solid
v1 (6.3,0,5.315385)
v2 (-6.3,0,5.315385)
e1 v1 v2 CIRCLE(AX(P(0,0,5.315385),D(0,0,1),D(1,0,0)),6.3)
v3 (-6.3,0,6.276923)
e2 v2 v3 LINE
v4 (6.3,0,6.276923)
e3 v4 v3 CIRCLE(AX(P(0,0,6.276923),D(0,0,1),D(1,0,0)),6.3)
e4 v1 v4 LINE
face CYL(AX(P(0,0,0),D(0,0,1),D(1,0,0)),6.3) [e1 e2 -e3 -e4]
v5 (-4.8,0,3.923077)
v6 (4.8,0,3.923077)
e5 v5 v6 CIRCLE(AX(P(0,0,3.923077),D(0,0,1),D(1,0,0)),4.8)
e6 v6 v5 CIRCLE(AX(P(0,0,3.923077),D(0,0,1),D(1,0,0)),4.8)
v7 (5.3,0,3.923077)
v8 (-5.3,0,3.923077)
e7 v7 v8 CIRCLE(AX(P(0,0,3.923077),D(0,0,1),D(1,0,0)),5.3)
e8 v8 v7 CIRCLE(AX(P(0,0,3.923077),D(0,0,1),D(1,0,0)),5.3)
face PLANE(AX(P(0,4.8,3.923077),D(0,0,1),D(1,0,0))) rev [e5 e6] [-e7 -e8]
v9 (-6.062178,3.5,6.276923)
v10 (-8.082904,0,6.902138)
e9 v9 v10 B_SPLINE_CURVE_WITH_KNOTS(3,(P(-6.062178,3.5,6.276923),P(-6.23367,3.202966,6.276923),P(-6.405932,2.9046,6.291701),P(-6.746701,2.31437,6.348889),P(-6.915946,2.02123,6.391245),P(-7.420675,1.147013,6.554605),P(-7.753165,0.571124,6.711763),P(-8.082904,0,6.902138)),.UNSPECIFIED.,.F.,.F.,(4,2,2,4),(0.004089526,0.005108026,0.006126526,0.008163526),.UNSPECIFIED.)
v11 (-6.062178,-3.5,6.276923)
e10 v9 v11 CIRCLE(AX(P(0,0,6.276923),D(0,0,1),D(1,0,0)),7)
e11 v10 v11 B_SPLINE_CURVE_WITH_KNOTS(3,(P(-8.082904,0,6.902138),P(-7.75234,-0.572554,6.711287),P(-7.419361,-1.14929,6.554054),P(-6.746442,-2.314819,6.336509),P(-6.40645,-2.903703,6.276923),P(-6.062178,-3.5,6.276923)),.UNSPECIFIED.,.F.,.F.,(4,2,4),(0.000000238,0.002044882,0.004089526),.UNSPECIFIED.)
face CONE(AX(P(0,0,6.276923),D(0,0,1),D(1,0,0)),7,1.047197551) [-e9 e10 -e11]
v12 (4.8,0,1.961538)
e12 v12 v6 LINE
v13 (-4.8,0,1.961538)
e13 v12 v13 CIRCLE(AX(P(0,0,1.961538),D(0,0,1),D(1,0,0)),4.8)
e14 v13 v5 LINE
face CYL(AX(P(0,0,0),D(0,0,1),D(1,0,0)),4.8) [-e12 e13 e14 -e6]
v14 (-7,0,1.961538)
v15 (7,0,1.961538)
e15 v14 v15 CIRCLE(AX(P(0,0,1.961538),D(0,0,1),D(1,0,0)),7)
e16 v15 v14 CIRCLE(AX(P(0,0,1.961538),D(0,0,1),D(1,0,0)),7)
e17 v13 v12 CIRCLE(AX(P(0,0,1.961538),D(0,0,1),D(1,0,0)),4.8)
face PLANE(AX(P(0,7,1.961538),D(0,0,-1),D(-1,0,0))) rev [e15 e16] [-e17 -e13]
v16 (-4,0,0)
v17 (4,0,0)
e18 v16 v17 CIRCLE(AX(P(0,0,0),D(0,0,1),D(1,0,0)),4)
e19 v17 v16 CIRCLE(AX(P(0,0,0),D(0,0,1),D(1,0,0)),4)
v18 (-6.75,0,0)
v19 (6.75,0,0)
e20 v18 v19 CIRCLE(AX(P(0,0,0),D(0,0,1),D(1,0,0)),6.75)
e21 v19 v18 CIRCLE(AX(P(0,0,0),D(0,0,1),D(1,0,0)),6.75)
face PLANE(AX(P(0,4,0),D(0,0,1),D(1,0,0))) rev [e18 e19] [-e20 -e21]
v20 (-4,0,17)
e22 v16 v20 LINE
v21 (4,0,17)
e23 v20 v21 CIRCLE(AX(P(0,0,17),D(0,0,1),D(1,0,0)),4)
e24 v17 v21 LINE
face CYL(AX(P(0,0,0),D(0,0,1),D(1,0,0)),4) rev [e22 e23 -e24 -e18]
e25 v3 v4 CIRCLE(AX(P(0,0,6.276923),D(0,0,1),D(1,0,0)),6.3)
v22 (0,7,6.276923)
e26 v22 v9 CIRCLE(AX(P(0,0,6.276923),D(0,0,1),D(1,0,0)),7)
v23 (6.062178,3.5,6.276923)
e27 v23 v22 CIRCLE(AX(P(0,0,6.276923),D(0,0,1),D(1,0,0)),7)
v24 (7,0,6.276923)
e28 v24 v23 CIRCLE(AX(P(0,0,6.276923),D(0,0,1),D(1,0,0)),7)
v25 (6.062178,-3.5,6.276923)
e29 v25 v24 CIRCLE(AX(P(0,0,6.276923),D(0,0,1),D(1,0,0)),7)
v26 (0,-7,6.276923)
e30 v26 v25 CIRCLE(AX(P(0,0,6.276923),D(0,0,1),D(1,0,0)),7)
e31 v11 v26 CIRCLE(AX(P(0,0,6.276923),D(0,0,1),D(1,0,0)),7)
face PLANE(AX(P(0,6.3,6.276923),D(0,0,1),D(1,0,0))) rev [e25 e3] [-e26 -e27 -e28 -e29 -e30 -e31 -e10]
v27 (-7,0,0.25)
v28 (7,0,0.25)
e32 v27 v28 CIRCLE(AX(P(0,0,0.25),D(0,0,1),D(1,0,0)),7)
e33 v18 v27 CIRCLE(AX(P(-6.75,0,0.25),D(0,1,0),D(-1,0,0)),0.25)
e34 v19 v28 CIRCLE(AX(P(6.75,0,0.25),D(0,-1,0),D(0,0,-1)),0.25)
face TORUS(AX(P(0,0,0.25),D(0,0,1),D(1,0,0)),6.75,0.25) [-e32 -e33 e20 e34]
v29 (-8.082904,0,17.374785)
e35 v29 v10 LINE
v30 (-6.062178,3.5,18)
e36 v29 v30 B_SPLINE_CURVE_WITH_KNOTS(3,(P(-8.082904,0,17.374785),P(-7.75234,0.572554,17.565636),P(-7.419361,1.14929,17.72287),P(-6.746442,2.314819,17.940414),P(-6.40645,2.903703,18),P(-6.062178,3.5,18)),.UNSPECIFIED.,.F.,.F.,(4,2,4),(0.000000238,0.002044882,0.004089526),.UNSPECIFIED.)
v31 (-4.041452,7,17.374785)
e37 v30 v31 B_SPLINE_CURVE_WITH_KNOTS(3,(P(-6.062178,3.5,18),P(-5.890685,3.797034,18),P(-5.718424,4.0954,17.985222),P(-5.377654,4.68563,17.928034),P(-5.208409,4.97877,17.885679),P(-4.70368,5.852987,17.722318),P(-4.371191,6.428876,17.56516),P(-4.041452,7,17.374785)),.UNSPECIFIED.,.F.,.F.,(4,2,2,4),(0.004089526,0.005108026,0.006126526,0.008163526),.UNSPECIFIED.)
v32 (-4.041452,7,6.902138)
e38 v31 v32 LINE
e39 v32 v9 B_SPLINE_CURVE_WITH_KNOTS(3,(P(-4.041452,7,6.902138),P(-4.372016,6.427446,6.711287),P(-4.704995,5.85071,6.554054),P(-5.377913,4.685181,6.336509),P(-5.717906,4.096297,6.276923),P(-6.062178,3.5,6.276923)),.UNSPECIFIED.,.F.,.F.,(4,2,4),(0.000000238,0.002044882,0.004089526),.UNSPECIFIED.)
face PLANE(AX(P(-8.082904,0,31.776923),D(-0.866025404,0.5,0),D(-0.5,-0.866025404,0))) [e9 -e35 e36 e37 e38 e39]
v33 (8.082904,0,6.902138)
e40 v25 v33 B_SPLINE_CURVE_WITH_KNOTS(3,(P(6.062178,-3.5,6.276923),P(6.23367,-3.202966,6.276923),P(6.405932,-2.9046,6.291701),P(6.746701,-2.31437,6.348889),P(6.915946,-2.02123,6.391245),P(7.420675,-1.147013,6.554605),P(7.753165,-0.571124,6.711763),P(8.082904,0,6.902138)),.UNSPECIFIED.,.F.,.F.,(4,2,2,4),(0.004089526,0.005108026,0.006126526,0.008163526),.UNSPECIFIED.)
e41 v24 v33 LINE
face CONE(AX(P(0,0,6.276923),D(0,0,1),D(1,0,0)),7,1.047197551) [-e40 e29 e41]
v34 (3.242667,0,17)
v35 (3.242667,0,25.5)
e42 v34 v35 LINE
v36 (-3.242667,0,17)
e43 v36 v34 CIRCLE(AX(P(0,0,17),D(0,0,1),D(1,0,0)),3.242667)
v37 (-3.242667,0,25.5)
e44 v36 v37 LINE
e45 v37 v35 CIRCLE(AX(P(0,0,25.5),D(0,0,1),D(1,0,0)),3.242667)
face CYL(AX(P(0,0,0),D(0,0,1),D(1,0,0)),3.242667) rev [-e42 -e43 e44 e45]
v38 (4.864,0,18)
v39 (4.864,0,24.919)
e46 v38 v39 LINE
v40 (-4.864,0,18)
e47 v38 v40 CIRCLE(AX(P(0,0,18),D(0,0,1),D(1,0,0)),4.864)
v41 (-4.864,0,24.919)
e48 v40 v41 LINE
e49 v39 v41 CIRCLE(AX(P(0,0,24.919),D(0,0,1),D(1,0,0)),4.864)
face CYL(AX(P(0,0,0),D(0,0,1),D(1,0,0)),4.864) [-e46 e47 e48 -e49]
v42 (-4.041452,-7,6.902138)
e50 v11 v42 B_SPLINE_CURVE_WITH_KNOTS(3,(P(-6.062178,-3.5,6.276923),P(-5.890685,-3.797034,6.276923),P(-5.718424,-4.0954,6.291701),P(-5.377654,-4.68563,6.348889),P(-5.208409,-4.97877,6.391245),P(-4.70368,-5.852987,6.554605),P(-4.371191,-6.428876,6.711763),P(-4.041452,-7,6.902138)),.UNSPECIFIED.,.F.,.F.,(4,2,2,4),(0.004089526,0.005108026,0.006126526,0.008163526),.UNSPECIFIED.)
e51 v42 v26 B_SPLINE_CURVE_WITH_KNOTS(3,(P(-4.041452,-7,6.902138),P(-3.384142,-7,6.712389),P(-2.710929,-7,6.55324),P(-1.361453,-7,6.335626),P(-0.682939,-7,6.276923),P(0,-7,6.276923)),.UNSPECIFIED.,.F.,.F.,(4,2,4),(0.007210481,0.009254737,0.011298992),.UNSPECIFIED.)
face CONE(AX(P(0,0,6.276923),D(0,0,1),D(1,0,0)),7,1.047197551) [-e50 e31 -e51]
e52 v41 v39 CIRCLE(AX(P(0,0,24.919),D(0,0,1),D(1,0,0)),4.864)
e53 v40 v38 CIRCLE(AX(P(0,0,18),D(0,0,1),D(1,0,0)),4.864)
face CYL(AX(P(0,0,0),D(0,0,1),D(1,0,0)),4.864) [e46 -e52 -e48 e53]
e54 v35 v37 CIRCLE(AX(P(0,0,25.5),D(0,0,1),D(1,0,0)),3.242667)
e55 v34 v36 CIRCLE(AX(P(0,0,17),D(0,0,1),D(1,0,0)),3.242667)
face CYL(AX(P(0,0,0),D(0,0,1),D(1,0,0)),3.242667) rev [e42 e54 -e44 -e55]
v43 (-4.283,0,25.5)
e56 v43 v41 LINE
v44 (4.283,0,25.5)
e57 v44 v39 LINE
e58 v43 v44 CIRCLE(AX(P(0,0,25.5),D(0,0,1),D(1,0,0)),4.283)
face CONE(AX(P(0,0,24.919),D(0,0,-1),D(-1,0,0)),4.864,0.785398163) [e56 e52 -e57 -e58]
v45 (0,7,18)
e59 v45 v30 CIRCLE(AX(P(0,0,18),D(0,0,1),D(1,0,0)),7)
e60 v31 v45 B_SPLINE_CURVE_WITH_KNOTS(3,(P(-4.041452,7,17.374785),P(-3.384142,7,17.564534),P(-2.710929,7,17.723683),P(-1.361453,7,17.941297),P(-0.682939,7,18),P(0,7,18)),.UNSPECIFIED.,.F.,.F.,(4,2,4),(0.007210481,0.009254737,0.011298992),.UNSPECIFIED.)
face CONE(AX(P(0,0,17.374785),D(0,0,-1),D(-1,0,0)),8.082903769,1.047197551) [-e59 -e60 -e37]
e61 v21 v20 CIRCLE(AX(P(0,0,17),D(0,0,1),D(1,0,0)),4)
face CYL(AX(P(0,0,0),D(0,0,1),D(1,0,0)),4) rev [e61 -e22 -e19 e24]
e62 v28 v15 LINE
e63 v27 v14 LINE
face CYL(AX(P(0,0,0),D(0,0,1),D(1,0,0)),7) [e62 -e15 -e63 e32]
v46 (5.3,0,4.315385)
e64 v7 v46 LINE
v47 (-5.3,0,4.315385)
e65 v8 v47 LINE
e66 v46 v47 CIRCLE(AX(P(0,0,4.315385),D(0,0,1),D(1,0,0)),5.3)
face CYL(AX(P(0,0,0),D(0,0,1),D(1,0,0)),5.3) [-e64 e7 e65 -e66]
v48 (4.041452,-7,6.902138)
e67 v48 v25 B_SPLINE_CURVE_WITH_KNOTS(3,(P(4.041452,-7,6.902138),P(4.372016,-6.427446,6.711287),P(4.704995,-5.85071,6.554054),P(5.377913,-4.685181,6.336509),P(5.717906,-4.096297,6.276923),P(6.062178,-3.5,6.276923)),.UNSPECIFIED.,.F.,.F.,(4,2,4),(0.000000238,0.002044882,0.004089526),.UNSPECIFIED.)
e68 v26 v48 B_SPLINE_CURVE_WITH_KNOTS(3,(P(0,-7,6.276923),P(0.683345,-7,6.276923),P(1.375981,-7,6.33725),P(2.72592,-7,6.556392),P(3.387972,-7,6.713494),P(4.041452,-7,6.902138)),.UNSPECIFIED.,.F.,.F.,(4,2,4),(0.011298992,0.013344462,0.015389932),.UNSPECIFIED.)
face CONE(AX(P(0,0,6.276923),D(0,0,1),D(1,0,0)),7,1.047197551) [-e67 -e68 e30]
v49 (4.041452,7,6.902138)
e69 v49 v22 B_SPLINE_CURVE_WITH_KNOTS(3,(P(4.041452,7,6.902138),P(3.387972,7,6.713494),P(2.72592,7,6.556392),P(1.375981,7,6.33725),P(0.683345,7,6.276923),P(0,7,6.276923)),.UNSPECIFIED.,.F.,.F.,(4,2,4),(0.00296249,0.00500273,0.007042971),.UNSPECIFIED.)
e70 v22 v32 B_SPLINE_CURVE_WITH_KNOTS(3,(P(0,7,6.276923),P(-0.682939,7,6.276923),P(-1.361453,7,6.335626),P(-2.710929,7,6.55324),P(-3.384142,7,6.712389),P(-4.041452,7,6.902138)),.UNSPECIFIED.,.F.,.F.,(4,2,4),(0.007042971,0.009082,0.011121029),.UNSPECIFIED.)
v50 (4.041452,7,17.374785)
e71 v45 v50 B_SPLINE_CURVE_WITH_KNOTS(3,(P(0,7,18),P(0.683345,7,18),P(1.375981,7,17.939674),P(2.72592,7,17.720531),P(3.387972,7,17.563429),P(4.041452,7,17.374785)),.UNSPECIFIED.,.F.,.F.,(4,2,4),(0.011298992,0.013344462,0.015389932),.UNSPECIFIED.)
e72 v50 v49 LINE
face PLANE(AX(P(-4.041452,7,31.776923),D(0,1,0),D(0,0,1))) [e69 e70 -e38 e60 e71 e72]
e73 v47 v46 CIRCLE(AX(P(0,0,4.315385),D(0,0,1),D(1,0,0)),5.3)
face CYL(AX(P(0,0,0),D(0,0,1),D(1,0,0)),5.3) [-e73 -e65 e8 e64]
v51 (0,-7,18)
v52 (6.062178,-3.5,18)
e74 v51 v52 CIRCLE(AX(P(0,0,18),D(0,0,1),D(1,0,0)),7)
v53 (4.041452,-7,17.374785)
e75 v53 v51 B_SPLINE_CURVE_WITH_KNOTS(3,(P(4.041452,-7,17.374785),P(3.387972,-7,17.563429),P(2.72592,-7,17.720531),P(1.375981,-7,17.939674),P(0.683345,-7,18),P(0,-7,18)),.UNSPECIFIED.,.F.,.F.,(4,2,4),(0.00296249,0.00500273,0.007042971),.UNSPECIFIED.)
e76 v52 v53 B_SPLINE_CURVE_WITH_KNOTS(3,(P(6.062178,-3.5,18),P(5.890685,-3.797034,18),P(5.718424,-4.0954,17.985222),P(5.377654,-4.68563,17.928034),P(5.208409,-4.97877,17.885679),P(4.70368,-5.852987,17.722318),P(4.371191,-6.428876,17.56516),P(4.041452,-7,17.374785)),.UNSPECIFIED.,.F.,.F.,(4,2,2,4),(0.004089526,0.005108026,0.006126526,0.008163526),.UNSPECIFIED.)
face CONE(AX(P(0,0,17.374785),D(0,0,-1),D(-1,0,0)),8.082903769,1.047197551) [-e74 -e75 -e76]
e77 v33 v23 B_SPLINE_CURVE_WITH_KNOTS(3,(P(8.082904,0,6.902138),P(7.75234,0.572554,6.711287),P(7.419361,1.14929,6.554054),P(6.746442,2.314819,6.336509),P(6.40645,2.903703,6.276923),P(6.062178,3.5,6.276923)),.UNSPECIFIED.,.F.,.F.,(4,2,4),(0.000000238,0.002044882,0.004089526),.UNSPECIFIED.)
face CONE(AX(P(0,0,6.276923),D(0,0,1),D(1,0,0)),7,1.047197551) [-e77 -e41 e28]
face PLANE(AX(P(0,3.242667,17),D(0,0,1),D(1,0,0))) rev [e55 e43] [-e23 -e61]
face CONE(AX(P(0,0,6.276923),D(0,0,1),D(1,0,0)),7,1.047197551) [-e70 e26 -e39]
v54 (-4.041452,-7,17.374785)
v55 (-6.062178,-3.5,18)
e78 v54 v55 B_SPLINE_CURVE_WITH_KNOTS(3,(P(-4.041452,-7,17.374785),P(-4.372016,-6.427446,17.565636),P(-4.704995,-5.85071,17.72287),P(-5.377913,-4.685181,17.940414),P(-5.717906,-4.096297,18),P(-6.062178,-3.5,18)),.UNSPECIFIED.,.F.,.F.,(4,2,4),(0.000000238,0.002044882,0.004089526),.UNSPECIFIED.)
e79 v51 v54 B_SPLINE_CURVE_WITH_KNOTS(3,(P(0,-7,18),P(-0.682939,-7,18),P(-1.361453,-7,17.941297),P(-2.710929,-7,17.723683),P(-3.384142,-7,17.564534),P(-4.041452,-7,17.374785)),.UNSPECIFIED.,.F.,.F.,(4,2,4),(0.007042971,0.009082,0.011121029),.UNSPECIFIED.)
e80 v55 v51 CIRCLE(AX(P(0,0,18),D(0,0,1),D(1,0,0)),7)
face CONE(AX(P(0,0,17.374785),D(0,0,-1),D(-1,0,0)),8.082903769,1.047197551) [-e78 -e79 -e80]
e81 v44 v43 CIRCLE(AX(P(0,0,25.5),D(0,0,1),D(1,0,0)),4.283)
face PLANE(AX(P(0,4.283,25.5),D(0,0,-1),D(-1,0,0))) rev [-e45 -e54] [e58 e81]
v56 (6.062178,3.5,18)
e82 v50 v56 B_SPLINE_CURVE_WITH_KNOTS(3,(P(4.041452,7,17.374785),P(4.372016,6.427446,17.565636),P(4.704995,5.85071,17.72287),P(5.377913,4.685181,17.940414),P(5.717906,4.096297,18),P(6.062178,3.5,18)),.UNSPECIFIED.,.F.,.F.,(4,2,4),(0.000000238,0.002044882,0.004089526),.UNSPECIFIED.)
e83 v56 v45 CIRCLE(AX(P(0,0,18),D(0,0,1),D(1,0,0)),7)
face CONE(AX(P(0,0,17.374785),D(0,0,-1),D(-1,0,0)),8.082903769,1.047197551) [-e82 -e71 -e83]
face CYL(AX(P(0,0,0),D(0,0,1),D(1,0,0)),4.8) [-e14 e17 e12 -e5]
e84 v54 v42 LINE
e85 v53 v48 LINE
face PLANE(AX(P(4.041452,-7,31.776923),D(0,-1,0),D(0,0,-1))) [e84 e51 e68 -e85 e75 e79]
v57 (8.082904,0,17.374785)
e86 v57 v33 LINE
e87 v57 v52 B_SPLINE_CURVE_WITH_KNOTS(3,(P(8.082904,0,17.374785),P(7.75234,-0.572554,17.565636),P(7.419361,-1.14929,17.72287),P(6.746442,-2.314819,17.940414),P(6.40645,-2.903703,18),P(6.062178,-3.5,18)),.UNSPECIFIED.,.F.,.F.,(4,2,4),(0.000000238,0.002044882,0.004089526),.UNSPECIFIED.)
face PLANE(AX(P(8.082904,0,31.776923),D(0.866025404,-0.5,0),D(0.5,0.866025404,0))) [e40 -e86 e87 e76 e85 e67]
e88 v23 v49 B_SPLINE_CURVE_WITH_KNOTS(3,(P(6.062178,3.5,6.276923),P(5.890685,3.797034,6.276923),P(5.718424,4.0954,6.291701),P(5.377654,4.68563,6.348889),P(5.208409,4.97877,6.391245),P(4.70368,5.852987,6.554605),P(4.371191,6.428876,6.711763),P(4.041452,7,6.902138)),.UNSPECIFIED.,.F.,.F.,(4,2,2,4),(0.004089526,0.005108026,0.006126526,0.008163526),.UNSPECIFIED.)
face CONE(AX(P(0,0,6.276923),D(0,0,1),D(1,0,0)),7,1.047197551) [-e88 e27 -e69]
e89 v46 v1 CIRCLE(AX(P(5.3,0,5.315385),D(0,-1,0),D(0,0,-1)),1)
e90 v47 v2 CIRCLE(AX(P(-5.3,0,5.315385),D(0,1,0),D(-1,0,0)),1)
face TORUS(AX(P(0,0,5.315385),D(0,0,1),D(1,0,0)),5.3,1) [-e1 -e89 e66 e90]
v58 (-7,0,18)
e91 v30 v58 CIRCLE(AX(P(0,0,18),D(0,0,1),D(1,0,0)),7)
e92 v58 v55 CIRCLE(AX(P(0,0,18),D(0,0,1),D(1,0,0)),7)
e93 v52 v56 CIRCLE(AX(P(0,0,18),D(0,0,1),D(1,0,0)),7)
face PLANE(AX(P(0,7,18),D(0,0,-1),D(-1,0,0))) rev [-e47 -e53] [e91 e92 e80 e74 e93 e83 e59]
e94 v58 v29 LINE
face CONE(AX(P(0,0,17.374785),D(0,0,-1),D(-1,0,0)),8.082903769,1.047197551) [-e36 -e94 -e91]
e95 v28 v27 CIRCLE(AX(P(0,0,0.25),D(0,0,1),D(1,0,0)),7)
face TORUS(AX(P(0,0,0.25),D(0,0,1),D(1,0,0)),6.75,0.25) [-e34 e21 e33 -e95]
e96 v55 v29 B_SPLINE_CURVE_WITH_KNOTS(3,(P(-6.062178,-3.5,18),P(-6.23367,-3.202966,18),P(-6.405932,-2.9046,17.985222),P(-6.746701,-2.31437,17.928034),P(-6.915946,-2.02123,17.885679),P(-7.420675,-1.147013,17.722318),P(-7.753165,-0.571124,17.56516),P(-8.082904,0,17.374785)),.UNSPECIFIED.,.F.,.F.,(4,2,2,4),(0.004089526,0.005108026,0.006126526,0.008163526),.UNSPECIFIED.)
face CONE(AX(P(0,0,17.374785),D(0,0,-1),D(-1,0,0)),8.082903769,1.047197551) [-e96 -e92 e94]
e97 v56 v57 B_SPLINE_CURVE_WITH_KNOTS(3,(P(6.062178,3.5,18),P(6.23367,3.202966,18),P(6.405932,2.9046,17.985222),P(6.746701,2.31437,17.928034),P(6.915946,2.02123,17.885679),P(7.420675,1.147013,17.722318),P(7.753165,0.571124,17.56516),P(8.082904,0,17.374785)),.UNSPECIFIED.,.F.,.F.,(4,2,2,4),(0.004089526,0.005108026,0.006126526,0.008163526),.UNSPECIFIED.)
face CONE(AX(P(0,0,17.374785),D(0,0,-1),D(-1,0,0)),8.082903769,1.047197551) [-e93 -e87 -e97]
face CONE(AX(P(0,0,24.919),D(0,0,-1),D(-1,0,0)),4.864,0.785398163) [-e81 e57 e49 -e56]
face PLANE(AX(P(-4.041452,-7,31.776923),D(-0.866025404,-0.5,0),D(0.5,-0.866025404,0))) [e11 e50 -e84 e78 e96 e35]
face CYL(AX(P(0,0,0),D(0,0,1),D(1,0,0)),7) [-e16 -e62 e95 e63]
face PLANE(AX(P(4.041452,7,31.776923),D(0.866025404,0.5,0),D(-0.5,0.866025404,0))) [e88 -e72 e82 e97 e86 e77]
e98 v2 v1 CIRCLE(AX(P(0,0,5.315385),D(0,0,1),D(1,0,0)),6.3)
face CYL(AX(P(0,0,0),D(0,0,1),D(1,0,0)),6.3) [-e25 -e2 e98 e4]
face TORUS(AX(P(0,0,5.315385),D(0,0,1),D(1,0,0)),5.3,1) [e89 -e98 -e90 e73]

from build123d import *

# Parameters (mm, degrees)
SKETCH_2_R          = 14
CUT_EXTRUDE_1_DEPTH = 25.5


with BuildPart() as part:
    # 草图1 → 旋转1 (revolve)
    with BuildSketch(Plane(origin=(0, 0, 0), x_dir=(0, 0, -1), z_dir=(1, 0, 0)), mode=Mode.PRIVATE) as revolve_1_sk:
        with BuildLine():
            Line((-25.5, 3.242666667), (-17, 3.242666667))
            Line((-17, 3.242666667), (-17, 4))
            Line((-17, 4), (0, 4))
            Line((0, 4), (0, 6.75))
            ThreePointArc((0, 6.75), (-0.073223305, 6.926776695), (-0.25, 7))
            Line((-0.25, 7), (-1.961538462, 7))
            Line((-1.961538462, 7), (-1.961538462, 4.8))
            Line((-1.961538462, 4.8), (-3.923076923, 4.8))
            Line((-3.923076923, 4.8), (-3.923076923, 5.3))
            Line((-3.923076923, 5.3), (-4.315384615, 5.3))
            ThreePointArc((-4.315384615, 5.3), (-4.608277834, 6.007106781), (-5.315384615, 6.3))
            Line((-5.315384615, 6.3), (-6.276923077, 6.3))
            Line((-6.276923077, 6.3), (-6.276923077, 7))
            Line((-6.276923077, 7), (-6.902137859, 8.082903769))
            Line((-6.902137859, 8.082903769), (-17.374785218, 8.082903769))
            Line((-17.374785218, 8.082903769), (-18, 7))
            Line((-18, 7), (-18, 4.864))
            Line((-18, 4.864), (-24.919, 4.864))
            Line((-24.919, 4.864), (-25.5, 4.283))
            Line((-25.5, 4.283), (-25.5, 3.242666667))
        make_face()
    revolve(revolve_1_sk.sketch.rotate(Axis((0, 0, 0), (0, 0, 1)), 270), axis=Axis((0, 0, 0), (0, 0, 1)))

    # 草图2 → 切除-拉伸1 (cut)
    with BuildSketch(Plane(origin=(0, 0, 6.276923077), x_dir=(-1, 0, 0), z_dir=(0, 0, -1))):
        Circle(SKETCH_2_R)
        Polygon((-4.041451884, -7), (4.041451884, -7), (8.082903769, 0), (4.041451884, 7), (-4.041451884, 7), (-8.082903769, 0), align=None, mode=Mode.SUBTRACT)
    extrude(amount=-CUT_EXTRUDE_1_DEPTH, mode=Mode.SUBTRACT)


solid = part.part
